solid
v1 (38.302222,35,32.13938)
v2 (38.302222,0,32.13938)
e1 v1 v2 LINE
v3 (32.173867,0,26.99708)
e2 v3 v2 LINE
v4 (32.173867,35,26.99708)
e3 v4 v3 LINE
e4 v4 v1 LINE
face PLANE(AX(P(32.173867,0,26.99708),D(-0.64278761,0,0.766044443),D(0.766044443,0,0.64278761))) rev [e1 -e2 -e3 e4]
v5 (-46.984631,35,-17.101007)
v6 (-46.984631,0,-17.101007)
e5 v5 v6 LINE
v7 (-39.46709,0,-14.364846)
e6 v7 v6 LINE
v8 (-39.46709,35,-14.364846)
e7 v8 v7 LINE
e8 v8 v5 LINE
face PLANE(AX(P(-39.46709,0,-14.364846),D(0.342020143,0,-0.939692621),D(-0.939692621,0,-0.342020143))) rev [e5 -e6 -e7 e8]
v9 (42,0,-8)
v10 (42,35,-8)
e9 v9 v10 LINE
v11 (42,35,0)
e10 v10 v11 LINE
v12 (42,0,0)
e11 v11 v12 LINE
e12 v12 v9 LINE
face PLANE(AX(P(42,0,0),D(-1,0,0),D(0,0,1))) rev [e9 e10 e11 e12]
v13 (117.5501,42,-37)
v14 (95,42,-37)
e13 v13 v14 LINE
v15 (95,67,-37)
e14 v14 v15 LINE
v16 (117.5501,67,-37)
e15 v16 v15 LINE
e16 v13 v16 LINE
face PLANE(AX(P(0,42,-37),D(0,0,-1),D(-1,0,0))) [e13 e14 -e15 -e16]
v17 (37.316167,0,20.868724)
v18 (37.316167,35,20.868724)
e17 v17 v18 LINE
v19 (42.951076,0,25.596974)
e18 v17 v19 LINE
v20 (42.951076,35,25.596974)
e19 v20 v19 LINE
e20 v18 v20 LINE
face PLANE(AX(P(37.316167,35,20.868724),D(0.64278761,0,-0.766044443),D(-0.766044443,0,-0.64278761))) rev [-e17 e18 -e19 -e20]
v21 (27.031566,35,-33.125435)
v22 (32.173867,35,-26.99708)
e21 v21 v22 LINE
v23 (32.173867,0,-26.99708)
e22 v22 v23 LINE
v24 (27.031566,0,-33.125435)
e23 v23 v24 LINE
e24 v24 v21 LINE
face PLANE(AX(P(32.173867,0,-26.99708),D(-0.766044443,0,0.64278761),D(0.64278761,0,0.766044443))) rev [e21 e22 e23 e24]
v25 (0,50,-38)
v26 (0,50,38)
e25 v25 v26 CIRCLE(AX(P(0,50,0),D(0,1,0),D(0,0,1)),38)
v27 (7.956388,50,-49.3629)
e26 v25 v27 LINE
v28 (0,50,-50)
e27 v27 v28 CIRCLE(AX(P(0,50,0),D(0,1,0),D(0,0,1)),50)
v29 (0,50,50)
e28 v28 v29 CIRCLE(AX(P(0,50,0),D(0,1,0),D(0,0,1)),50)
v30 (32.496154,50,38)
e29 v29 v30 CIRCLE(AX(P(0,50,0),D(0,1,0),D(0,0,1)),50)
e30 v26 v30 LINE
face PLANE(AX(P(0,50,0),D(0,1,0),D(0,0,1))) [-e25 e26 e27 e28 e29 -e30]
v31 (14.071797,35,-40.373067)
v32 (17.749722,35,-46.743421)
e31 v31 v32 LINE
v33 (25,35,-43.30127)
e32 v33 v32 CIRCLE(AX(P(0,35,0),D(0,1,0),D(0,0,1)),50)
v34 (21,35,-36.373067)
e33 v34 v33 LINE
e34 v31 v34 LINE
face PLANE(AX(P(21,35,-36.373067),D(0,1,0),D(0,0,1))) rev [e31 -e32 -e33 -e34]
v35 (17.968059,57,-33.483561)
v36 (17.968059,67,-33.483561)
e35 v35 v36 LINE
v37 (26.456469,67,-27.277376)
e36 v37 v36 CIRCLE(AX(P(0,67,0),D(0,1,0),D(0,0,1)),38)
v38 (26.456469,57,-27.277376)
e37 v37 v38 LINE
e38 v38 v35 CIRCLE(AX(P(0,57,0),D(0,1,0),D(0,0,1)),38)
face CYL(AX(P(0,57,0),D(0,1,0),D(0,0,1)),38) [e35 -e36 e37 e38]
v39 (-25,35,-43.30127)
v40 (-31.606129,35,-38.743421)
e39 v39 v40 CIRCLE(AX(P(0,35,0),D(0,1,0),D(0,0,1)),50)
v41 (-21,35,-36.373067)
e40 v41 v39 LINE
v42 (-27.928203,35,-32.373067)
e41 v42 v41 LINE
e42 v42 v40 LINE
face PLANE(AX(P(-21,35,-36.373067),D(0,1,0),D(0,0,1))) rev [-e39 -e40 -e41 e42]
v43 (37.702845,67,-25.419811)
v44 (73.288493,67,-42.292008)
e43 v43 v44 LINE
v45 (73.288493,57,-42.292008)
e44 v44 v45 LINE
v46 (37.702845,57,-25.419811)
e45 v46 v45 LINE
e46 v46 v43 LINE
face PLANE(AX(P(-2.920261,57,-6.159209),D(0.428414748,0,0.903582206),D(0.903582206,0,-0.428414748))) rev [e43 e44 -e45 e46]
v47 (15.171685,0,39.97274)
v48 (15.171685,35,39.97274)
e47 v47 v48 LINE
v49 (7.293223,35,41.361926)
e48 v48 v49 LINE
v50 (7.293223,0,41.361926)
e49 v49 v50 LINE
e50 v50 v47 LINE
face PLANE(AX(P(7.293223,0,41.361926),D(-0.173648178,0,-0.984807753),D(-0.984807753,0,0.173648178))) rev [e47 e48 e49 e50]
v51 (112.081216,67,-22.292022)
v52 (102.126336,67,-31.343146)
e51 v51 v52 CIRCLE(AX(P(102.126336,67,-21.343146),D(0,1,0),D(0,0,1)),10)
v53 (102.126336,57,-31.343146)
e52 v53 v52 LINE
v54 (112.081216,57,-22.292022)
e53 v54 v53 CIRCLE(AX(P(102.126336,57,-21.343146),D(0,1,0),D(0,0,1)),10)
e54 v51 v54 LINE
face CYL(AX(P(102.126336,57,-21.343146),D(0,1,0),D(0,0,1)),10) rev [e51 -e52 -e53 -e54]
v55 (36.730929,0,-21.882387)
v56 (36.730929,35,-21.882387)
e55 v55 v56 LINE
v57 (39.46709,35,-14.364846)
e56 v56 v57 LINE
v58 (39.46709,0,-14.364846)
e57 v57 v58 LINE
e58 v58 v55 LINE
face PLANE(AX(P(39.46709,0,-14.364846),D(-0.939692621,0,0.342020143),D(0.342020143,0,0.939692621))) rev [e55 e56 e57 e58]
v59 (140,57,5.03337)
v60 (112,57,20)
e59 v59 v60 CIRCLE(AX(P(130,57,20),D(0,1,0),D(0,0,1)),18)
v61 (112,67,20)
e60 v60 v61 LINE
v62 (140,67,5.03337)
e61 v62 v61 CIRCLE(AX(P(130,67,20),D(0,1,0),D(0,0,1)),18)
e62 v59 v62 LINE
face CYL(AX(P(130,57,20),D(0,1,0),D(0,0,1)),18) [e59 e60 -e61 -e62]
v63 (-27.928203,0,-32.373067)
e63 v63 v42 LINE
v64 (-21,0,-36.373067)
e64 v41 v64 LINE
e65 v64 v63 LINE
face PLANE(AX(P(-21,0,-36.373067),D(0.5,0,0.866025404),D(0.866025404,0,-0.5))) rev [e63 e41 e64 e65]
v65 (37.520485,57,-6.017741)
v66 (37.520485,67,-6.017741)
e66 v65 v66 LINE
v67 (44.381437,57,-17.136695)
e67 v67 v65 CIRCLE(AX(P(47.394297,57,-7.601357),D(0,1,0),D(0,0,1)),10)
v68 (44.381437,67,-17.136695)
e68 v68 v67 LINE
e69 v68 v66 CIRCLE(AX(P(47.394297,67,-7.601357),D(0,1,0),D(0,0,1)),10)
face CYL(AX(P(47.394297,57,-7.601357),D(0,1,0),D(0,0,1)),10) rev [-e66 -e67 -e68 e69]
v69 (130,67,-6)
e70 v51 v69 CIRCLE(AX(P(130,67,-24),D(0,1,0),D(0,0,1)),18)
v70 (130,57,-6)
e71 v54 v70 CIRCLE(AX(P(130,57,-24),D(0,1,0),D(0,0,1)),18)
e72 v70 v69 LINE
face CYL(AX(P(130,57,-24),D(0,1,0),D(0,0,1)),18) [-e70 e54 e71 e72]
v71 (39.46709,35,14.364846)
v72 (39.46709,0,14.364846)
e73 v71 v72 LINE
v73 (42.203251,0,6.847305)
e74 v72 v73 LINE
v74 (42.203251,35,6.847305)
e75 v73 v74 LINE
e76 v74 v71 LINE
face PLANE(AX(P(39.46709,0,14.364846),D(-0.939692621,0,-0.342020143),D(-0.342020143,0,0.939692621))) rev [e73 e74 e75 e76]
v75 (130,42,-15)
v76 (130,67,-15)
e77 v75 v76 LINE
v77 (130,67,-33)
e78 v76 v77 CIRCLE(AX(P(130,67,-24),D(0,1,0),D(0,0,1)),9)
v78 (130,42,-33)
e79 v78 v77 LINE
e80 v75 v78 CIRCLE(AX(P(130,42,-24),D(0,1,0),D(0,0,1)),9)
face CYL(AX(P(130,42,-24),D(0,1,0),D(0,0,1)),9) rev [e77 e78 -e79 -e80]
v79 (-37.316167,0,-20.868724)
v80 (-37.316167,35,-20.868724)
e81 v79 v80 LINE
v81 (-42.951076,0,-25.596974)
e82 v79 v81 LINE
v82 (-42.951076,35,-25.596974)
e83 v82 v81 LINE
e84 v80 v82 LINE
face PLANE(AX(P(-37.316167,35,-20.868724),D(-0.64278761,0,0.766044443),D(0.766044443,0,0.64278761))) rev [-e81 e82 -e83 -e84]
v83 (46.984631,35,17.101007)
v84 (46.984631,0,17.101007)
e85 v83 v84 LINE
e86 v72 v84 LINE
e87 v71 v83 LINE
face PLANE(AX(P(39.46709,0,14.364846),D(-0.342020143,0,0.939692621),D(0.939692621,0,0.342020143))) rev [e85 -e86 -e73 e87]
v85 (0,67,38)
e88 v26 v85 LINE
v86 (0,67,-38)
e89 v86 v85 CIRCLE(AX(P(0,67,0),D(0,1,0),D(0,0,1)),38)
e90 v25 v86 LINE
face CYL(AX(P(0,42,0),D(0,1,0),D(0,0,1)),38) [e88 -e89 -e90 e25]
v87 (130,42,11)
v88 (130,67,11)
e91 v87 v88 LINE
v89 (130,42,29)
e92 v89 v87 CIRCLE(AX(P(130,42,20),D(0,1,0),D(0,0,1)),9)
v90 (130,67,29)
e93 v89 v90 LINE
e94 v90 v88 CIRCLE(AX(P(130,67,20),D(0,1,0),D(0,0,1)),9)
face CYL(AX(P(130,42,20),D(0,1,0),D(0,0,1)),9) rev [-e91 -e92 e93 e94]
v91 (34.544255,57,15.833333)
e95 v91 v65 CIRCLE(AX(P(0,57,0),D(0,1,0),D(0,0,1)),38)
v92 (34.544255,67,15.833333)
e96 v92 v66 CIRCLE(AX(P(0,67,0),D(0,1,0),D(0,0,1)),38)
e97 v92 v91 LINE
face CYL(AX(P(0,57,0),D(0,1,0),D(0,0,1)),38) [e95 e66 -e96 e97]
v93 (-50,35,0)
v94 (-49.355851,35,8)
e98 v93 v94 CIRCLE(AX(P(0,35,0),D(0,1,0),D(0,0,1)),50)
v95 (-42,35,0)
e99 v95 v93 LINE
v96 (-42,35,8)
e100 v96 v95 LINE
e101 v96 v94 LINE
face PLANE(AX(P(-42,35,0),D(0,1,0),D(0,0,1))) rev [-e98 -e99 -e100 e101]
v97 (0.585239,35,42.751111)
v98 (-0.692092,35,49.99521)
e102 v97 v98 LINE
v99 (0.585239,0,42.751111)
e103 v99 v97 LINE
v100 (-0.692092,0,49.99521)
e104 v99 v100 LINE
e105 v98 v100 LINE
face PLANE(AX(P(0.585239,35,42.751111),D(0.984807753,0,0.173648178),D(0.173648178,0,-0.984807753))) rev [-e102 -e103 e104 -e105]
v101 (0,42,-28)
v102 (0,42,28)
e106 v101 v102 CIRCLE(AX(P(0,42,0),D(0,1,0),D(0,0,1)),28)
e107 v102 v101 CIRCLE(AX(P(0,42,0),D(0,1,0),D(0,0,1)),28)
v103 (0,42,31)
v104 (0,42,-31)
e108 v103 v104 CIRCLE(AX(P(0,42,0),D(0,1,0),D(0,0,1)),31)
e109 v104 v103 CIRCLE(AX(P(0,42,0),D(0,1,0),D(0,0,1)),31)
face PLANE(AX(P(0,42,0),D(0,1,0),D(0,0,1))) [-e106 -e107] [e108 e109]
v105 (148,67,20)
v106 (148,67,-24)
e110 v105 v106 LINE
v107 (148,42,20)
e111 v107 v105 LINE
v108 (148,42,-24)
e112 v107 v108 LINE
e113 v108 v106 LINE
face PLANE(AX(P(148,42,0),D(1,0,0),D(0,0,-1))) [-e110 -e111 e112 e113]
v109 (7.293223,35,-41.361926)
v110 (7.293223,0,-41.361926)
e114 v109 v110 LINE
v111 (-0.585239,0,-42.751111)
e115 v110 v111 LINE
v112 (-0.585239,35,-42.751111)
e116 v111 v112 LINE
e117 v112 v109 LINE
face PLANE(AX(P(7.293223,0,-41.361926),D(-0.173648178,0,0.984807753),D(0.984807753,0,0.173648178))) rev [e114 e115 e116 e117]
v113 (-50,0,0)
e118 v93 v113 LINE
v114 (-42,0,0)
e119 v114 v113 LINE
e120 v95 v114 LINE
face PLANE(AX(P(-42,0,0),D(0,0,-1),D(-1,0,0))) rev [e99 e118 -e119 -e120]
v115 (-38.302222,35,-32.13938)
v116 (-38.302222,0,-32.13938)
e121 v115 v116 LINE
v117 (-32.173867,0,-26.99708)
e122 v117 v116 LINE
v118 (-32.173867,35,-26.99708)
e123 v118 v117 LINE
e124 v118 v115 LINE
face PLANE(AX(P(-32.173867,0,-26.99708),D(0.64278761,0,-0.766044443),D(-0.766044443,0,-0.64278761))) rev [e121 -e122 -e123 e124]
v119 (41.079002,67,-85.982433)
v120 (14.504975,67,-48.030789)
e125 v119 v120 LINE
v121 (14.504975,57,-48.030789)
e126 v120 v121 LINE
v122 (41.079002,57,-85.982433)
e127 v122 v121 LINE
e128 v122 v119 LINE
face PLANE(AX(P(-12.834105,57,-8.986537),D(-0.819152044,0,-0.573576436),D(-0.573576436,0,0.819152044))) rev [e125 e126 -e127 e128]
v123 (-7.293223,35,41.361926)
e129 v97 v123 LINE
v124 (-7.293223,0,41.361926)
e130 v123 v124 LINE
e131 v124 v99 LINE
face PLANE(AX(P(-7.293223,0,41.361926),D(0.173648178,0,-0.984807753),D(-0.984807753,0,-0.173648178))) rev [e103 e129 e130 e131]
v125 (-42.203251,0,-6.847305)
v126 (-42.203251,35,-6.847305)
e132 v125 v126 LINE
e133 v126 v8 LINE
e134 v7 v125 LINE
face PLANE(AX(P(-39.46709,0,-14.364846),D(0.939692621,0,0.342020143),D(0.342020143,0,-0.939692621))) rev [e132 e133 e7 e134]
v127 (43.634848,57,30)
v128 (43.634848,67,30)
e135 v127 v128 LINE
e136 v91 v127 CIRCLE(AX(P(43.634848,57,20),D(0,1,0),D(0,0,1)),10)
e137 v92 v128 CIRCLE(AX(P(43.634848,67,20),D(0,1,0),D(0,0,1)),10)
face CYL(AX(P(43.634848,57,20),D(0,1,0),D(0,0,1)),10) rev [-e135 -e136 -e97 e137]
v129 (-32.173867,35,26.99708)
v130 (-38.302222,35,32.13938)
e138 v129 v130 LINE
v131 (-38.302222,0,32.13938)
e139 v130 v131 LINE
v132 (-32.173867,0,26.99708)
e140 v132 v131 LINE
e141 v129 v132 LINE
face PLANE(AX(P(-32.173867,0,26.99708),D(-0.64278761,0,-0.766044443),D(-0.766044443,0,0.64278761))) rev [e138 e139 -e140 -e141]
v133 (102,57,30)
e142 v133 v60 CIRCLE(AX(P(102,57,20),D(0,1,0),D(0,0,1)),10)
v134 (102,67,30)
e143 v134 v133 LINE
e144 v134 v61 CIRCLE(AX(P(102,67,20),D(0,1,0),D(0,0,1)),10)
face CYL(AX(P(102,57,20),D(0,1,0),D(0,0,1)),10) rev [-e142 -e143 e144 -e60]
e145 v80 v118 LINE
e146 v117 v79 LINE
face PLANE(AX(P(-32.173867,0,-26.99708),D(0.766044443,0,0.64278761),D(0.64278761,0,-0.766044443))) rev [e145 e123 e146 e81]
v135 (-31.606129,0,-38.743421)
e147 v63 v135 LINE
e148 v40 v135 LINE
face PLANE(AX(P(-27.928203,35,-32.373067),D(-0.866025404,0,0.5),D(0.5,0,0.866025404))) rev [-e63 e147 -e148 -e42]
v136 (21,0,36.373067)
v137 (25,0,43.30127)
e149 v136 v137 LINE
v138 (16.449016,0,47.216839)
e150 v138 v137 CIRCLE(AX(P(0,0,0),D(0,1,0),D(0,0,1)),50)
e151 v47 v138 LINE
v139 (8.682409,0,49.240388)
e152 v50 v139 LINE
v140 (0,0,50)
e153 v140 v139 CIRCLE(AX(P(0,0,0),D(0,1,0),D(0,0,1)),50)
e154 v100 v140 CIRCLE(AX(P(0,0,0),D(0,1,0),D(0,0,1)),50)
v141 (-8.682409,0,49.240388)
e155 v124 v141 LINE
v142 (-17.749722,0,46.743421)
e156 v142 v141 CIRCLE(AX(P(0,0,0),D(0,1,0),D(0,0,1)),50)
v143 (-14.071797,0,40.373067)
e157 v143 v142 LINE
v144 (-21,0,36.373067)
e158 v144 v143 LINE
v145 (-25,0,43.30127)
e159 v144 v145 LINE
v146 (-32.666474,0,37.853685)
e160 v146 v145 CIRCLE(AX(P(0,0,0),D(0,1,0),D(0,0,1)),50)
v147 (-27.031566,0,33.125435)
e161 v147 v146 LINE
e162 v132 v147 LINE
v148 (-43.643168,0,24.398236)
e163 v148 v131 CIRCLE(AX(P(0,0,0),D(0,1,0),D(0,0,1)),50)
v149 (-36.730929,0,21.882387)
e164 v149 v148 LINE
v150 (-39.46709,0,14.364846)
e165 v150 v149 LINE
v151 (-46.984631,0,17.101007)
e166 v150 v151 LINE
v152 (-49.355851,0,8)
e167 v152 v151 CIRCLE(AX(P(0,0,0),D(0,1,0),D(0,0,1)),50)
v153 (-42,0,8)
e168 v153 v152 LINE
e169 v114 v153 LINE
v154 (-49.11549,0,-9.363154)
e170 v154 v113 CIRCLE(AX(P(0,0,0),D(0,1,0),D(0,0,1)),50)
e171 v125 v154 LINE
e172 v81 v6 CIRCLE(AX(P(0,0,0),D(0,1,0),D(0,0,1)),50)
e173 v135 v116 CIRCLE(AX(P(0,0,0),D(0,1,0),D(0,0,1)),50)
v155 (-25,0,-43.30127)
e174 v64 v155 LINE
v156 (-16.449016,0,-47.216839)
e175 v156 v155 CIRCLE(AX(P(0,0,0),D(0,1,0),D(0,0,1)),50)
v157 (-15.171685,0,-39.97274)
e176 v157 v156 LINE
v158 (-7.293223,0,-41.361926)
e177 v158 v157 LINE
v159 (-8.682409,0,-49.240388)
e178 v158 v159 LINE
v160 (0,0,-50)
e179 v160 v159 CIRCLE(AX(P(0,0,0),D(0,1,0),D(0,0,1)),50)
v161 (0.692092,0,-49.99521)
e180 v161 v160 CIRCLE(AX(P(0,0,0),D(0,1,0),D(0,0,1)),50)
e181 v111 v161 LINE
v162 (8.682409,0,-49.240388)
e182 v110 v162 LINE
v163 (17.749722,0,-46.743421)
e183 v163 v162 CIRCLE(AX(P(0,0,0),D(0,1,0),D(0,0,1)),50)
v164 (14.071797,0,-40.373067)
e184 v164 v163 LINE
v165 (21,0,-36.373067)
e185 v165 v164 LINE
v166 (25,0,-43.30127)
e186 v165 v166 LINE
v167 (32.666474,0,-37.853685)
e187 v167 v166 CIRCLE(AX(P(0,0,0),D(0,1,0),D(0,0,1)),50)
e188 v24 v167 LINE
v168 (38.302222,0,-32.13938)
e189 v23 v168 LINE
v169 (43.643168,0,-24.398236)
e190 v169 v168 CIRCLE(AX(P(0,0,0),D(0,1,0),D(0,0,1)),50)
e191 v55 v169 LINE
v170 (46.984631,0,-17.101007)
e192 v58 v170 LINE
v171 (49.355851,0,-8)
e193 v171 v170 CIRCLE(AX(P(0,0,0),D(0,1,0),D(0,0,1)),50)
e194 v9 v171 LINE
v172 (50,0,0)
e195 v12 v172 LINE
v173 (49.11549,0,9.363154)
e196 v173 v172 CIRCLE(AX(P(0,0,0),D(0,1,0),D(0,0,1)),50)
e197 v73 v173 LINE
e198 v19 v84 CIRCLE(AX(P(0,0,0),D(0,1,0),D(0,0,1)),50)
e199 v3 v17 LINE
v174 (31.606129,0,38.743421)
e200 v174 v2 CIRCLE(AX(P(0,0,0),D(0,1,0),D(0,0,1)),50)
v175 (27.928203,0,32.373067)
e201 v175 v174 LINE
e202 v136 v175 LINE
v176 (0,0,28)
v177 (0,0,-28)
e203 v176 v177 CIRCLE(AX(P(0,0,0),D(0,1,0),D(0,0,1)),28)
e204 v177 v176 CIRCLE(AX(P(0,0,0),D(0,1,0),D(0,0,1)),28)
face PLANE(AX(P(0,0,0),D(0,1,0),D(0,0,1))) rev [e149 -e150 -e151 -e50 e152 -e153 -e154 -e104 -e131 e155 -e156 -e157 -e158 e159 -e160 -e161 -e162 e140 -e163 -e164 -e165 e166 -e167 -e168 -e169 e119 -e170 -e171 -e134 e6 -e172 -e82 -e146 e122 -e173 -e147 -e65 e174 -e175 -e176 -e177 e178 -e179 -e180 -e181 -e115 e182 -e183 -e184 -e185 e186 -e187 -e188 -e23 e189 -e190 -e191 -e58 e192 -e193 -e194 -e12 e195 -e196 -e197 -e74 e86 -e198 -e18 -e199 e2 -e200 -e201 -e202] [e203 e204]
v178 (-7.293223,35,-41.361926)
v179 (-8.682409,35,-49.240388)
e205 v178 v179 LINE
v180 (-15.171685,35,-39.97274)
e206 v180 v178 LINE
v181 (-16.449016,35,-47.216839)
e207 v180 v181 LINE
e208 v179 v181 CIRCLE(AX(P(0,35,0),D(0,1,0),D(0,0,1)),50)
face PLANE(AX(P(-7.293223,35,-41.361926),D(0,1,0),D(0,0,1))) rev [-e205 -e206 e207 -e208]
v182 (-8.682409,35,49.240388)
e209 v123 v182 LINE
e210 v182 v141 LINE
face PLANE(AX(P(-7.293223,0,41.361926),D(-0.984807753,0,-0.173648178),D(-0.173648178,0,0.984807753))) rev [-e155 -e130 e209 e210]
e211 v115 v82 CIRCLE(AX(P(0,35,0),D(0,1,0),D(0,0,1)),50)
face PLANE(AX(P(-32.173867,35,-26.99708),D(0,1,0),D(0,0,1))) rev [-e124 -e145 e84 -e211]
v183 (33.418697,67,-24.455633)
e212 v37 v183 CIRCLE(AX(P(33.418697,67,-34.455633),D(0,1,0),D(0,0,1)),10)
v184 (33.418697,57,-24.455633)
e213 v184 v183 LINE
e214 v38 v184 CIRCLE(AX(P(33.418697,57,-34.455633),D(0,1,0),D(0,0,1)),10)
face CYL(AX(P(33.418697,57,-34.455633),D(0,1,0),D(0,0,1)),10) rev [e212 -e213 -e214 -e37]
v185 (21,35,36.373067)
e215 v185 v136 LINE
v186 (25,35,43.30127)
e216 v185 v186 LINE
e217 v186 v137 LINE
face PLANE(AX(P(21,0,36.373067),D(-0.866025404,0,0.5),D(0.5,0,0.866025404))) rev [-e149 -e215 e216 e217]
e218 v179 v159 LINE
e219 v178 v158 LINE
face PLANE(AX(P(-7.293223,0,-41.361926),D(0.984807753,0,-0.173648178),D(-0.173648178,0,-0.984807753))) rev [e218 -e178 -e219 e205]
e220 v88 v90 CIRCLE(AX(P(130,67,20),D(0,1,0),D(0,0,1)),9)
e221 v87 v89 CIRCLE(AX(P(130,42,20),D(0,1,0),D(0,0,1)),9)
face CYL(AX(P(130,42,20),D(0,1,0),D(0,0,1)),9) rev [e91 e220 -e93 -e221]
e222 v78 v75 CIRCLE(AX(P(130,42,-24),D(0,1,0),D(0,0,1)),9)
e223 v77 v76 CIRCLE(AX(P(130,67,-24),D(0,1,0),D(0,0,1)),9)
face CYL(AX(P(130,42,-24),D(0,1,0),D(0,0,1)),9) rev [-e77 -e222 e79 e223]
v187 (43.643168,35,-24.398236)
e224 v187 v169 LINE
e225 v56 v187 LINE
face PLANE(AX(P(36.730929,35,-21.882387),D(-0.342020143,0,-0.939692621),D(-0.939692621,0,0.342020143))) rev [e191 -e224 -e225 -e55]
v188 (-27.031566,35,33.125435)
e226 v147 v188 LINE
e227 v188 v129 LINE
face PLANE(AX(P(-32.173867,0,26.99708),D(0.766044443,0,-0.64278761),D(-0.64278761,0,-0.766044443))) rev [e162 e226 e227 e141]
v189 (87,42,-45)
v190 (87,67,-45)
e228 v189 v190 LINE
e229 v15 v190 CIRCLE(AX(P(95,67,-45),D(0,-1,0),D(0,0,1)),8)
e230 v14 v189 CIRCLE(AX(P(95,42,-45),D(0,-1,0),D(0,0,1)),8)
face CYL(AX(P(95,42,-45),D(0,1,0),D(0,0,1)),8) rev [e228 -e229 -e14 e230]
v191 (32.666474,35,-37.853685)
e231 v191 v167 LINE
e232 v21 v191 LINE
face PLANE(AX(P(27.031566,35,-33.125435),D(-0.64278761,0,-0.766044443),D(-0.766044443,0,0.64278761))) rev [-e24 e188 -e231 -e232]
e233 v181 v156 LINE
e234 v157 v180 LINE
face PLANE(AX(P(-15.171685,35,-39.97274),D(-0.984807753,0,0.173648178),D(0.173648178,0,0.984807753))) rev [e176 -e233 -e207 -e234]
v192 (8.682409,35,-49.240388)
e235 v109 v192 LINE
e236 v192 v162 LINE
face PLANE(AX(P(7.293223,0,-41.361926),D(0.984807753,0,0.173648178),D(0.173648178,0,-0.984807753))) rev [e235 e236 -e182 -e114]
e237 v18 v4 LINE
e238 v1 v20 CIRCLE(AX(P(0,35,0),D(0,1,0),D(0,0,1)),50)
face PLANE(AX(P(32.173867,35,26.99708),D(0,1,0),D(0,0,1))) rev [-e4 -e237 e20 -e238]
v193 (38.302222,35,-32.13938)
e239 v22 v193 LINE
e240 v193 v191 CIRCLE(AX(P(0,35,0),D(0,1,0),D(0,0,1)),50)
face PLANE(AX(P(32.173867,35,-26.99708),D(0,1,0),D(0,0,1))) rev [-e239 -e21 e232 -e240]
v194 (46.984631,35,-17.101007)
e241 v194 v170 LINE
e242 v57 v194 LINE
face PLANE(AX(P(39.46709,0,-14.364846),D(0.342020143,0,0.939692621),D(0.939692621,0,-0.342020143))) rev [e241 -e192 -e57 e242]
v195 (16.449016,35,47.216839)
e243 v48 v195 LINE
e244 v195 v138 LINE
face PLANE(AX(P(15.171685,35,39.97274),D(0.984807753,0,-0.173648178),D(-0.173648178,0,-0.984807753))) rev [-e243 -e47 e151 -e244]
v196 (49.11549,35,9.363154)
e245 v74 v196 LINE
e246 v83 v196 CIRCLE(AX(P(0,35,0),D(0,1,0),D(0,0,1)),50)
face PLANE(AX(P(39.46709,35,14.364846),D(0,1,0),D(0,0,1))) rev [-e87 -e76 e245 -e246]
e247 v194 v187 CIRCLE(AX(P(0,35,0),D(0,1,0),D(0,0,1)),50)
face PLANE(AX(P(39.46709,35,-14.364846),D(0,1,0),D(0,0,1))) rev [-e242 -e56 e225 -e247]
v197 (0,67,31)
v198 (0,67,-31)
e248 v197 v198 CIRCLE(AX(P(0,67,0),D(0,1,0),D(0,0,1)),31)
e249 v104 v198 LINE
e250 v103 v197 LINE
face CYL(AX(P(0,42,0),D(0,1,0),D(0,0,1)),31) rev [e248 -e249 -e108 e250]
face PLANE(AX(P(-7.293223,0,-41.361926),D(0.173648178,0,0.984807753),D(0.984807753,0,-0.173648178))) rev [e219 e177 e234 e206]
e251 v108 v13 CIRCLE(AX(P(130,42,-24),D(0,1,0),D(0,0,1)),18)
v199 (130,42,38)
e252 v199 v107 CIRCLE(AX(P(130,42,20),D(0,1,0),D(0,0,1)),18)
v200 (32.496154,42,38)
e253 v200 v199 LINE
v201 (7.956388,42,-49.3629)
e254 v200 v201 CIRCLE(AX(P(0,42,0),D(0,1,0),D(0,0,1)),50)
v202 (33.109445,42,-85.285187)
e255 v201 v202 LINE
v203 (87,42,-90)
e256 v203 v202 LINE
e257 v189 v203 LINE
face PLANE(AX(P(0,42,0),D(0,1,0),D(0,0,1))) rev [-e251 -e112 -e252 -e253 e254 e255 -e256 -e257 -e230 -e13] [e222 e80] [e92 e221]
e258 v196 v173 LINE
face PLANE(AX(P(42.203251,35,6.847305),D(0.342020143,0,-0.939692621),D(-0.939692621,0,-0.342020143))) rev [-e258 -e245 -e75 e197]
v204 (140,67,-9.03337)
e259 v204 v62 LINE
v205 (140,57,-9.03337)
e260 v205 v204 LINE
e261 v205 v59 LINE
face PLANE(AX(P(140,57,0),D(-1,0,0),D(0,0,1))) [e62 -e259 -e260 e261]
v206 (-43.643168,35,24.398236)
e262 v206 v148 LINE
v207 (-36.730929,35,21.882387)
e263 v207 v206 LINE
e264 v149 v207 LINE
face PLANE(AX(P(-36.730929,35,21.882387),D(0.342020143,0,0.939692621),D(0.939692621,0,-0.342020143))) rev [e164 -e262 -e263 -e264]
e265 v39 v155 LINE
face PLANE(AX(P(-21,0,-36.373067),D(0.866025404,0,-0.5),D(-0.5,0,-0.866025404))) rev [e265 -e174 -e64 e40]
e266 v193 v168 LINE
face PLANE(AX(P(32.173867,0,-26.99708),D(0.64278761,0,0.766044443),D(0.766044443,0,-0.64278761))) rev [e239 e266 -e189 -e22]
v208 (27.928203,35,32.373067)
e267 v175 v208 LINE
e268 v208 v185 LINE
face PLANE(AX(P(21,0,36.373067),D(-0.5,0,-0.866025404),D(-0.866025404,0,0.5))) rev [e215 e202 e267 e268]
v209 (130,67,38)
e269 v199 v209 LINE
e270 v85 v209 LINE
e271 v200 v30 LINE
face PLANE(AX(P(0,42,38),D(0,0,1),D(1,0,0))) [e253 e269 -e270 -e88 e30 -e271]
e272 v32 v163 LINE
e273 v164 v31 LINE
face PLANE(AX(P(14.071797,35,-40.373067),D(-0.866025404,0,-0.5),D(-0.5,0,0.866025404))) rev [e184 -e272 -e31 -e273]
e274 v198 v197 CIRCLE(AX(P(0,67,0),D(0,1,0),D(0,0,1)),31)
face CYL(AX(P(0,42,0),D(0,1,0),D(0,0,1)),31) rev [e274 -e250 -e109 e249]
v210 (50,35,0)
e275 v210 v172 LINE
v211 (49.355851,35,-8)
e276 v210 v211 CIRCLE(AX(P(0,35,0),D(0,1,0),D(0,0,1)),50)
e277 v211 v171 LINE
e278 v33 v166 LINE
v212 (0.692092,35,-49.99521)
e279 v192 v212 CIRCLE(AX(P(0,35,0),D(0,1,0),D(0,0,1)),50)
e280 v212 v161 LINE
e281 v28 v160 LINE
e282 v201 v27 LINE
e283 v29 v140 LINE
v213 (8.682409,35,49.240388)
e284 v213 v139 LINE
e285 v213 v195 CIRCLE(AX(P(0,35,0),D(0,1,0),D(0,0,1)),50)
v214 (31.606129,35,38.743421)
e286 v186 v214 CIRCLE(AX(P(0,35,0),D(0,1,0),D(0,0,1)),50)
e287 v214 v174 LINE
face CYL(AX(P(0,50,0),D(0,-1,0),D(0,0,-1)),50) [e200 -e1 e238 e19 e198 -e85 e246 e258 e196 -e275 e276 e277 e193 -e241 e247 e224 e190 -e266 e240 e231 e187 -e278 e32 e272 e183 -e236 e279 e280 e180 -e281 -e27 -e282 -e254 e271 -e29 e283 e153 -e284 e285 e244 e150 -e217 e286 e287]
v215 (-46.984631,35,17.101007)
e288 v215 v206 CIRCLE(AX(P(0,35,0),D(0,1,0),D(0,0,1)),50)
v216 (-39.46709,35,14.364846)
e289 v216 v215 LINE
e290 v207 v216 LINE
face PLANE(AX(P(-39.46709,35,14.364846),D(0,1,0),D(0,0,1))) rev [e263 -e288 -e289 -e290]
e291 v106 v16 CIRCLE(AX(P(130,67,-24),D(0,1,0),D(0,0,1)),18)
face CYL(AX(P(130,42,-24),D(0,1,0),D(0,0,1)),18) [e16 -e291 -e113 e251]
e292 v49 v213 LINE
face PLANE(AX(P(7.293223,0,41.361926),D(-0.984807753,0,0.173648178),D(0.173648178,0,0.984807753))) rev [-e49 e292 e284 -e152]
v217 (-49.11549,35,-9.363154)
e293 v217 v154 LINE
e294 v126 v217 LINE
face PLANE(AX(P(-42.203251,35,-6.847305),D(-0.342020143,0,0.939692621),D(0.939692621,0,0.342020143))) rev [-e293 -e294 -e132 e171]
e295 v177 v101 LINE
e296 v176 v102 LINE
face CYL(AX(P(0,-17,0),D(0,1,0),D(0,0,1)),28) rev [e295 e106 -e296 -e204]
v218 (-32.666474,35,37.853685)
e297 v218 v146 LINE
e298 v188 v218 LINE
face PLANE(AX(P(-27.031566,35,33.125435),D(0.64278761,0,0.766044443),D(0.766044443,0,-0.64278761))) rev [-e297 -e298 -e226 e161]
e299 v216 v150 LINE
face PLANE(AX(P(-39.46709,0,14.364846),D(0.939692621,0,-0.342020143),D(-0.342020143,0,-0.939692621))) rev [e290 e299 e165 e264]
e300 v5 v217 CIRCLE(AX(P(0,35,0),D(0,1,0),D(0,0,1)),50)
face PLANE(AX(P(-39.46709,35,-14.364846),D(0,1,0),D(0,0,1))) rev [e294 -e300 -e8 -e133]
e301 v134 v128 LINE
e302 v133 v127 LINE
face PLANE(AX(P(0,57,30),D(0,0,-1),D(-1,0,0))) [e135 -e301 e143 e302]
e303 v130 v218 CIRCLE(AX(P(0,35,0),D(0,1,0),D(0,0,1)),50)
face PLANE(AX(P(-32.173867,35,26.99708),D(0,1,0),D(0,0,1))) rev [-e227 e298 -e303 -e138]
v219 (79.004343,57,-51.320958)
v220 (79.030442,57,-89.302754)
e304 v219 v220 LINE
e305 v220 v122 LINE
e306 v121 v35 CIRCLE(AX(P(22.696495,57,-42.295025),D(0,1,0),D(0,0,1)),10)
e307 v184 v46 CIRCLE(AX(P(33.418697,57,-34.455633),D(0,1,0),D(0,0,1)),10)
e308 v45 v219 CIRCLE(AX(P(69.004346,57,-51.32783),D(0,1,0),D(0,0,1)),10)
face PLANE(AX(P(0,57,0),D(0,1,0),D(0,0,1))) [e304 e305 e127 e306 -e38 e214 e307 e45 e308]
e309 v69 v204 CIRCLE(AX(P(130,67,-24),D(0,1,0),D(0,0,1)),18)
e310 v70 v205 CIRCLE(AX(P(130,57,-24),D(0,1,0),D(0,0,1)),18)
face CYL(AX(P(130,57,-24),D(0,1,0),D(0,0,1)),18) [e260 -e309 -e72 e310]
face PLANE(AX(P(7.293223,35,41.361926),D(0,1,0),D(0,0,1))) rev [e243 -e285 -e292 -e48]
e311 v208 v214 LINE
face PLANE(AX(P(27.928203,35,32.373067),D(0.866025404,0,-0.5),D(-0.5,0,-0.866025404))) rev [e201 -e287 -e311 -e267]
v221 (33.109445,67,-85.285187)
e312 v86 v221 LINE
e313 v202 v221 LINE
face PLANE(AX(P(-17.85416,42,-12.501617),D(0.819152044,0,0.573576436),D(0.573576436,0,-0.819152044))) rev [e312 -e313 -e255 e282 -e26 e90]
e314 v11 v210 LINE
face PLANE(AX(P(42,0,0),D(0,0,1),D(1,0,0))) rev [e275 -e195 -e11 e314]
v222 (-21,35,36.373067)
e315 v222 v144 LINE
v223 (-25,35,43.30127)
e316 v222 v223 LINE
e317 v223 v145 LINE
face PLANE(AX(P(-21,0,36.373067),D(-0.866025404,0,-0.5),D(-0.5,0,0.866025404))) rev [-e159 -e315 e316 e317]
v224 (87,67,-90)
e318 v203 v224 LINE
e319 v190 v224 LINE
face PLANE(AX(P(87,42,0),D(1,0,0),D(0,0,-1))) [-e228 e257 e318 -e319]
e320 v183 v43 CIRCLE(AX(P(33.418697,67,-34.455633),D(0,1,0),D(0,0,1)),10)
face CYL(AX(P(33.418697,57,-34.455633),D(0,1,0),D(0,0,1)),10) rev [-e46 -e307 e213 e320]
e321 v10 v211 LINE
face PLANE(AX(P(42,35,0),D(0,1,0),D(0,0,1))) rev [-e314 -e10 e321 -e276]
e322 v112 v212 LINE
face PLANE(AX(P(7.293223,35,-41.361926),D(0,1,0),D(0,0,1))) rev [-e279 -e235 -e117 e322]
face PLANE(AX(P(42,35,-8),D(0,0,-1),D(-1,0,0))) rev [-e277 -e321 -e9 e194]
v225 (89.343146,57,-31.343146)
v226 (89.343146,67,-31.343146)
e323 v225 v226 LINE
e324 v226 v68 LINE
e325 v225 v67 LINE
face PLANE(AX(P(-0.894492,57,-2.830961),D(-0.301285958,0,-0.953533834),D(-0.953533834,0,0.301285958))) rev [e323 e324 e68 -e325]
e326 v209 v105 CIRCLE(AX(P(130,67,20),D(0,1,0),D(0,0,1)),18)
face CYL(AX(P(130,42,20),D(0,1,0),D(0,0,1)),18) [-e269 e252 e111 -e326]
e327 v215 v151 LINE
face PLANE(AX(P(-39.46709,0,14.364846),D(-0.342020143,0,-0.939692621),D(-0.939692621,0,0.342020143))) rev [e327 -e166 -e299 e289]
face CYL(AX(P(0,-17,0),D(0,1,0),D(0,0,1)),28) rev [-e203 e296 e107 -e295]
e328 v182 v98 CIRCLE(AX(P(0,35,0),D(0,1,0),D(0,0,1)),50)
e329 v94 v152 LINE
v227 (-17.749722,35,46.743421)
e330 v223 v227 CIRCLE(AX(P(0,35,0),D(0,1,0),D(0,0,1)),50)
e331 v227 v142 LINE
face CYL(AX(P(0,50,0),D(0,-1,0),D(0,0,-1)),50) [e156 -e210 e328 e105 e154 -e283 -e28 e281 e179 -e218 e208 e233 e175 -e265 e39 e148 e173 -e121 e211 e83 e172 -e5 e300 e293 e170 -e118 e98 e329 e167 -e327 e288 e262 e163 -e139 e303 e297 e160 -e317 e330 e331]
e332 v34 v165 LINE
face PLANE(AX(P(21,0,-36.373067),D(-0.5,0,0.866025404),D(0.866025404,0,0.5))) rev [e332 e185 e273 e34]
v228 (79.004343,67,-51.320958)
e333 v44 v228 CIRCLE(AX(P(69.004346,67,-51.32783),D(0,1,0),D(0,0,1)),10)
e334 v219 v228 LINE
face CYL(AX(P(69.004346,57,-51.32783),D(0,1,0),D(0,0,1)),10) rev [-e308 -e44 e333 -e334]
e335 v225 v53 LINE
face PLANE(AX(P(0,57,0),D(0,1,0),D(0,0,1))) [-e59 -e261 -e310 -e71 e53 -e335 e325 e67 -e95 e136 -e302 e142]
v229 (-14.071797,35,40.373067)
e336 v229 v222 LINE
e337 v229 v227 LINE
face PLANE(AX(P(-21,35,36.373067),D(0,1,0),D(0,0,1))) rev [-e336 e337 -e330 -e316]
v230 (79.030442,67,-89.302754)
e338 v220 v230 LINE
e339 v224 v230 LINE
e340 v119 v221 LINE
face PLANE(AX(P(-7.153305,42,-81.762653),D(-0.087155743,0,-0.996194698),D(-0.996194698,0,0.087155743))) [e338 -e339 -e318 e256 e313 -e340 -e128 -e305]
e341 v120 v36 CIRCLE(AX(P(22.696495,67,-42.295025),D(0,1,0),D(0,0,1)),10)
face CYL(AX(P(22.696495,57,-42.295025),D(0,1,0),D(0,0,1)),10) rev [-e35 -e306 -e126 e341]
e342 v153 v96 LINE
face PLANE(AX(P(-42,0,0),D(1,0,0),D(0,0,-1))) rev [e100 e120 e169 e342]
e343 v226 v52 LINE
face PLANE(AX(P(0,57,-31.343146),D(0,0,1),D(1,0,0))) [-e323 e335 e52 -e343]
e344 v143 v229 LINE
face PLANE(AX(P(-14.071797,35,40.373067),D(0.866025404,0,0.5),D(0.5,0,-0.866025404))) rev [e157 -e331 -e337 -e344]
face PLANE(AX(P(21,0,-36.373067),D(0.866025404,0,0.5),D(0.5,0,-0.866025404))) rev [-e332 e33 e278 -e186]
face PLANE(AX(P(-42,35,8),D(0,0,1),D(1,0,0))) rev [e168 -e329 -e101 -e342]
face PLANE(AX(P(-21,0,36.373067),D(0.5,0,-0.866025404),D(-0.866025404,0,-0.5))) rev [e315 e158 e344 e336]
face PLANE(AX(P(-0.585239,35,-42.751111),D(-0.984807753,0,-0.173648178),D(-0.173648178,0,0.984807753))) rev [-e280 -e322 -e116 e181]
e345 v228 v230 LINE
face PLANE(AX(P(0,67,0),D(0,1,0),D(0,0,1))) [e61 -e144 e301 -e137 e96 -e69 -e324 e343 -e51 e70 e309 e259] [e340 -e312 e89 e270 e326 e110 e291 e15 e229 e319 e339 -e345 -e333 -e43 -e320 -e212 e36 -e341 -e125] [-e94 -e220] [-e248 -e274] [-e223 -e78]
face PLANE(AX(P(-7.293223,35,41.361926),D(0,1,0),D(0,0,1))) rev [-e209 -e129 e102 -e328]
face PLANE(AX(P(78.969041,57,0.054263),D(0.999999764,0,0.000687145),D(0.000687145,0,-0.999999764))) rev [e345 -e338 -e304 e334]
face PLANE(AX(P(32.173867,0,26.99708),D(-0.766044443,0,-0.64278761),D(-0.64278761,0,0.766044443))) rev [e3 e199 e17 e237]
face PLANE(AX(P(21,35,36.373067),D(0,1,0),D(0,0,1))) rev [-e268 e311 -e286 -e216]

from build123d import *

# Parameters (mm, degrees)
HUB_PROFILE_SKETCH_R            = 50
HUB_CYLINDER_DEPTH              = 50
GROOVE_PROFILE_SKETCH_W         = 8
GROOVE_PROFILE_SKETCH_H         = 35
RADIAL_GROOVE_DEPTH             = 8
RADIAL_GROOVE_PATTERN_18X_COUNT = 18
BRACKET_ARM_DEPTH               = 17
BRACKET_ARM_DEPTH_BACK          = 8
BRACKET_ARM_SKETCH_R            = 9
ARM_START                       = -10
ARM_POCKETS_DEPTH               = 10
HUB_COUNTERBORE_SKETCH_R        = 31
HUB_COUNTERBORE_DEPTH           = 25
HUB_THROUGH_BORE_SKETCH_R       = 28
HUB_THROUGH_BORE_DEPTH          = 59
POCKET_FILLET_R10_A_R           = 10
POCKET_FILLET_R10_B_R           = 10
POCKET_FILLET_R10_C_R           = 10
POCKET_FILLET_R10_D_R           = 10
POCKET_FILLET_R10_E_R           = 10
POCKET_FILLET_R10_F_R           = 10
POCKET_FILLET_R10_G_R           = 10


with BuildPart() as part:
    # Hub Profile Sketch → Hub Cylinder (new body)
    with BuildSketch(Plane(origin=(0, 0, 0), x_dir=(1, 0, 0), z_dir=(0, 1, 0))):
        with Locations(Location((0, 0, 0), (0, 0, 270))):
            Circle(HUB_PROFILE_SKETCH_R)
    extrude(amount=HUB_CYLINDER_DEPTH)

    # Groove Profile Sketch → Radial Groove (cut)
    with BuildSketch(Plane(origin=(50, 0, 0), x_dir=(0, 0, -1), z_dir=(1, 0, 0))):
        with Locations((4, 17.5)):
            Rectangle(GROOVE_PROFILE_SKETCH_W, GROOVE_PROFILE_SKETCH_H)
    radial_groove = extrude(amount=-RADIAL_GROOVE_DEPTH, mode=Mode.SUBTRACT)

    # Radial Groove Pattern 18x: Radial Groove ×18 about axis
    radial_groove_pattern_18x_axis = Axis((0, 0, 0), (0, 1, 0))
    for i in range(1, RADIAL_GROOVE_PATTERN_18X_COUNT):
        add(radial_groove.rotate(radial_groove_pattern_18x_axis, i * 360 / RADIAL_GROOVE_PATTERN_18X_COUNT), mode=Mode.SUBTRACT)

    # Bracket Arm Sketch → Bracket Arm (add, two sides: drawn at the far end of the back side and taken through both)
    with BuildSketch(Plane(origin=(0, 50, 0), x_dir=(1, 0, 0), z_dir=(0, 1, 0)).offset(-BRACKET_ARM_DEPTH_BACK)):
        with BuildLine():
            Line((33.109444616, 85.285187333), (0, 38))
            ThreePointArc((0, 38), (-38, 0), (0, -38))
            Line((0, -38), (130, -38))
            ThreePointArc((130, -38), (142.727922061, -32.727922061), (148, -20))
            Line((148, -20), (148, 24))
            ThreePointArc((148, 24), (137.067595321, 40.554428301), (117.550100402, 37))
            Line((117.550100402, 37), (95, 37))
            ThreePointArc((95, 37), (89.343145751, 39.343145751), (87, 45))
            Line((87, 45), (87, 90))
            Line((87, 90), (33.109444616, 85.285187333))
        make_face()
        with Locations(Location((130, -20, 0), (0, 0, 270))):
            Circle(BRACKET_ARM_SKETCH_R, mode=Mode.SUBTRACT)
        with Locations(Location((130, 24, 0), (0, 0, 270))):
            Circle(BRACKET_ARM_SKETCH_R, mode=Mode.SUBTRACT)
    extrude(amount=BRACKET_ARM_DEPTH + BRACKET_ARM_DEPTH_BACK)

    # Arm Pocket Sketch → Arm Pockets (cut)
    with BuildSketch(Plane(origin=(0, 67, 0), x_dir=(1, 0, 0), z_dir=(0, 1, 0)).offset(ARM_START)):
        with BuildLine():
            ThreePointArc((38, 0), (34.134327941, -16.698732167), (23.323807579, -30))
            Line((23.323807579, -30), (65, -30))
            Line((65, -30), (115.033370453, -30))
            ThreePointArc((115.033370453, -30), (117.272077939, -7.272077939), (140, -5.033370453))
            Line((140, -5.033370453), (140, 2))
            Line((140, 2), (140, 9.033370453))
            ThreePointArc((140, 9.033370453), (118.390487135, 10.244302597), (113.565943578, 31.343145751))
            Line((113.565943578, 31.343145751), (89.343145751, 31.343145751))
            Line((89.343145751, 31.343145751), (35.229033551, 14.244830468))
            ThreePointArc((35.229033551, 14.244830468), (37.30082623, 7.255919138), (38, 0))
        make_face()
        with BuildLine():
            Line((79.030442415, 89.302754058), (41.079002201, 85.982433275))
            Line((41.079002201, 85.982433275), (7.022974779, 37.345385595))
            ThreePointArc((7.022974779, 37.345385595), (20.403319818, 32.057831187), (30.858927169, 22.17490956))
            Line((30.858927169, 22.17490956), (79, 45))
            Line((79, 45), (79.030442415, 89.302754058))
        make_face()
    extrude(amount=ARM_POCKETS_DEPTH, mode=Mode.SUBTRACT)

    # Hub Counterbore Sketch → Hub Counterbore (cut)
    with BuildSketch(Plane(origin=(0, 67, 0), x_dir=(1, 0, 0), z_dir=(0, 1, 0))):
        with Locations(Location((0, 0, 0), (0, 0, 270))):
            Circle(HUB_COUNTERBORE_SKETCH_R)
    extrude(amount=-HUB_COUNTERBORE_DEPTH, mode=Mode.SUBTRACT)

    # Hub Through Bore Sketch → Hub Through Bore (cut)
    with BuildSketch(Plane(origin=(0, 42, 0), x_dir=(1, 0, 0), z_dir=(0, 1, 0))):
        with Locations(Location((0, 0, 0), (0, 0, 270))):
            Circle(HUB_THROUGH_BORE_SKETCH_R)
    extrude(amount=-HUB_THROUGH_BORE_DEPTH, mode=Mode.SUBTRACT)

    # Pocket Fillet R10 A
    pocket_fillet_r10_a_edges = [part.edges().sort_by_distance(p)[0] for p in [
        (23.323807579, 62, 30),
    ]]
    fillet(pocket_fillet_r10_a_edges, radius=POCKET_FILLET_R10_A_R)

    # Pocket Fillet R10 B
    pocket_fillet_r10_b_edges = [part.edges().sort_by_distance(p)[0] for p in [
        (115.033370453, 62, 30),
    ]]
    fillet(pocket_fillet_r10_b_edges, radius=POCKET_FILLET_R10_B_R)

    # Pocket Fillet R10 C
    pocket_fillet_r10_c_edges = [part.edges().sort_by_distance(p)[0] for p in [
        (113.565943578, 62, -31.343145751),
    ]]
    fillet(pocket_fillet_r10_c_edges, radius=POCKET_FILLET_R10_C_R)

    # Pocket Fillet R10 D
    pocket_fillet_r10_d_edges = [part.edges().sort_by_distance(p)[0] for p in [
        (35.229033551, 62, -14.244830468),
    ]]
    fillet(pocket_fillet_r10_d_edges, radius=POCKET_FILLET_R10_D_R)

    # Pocket Fillet R10 E
    pocket_fillet_r10_e_edges = [part.edges().sort_by_distance(p)[0] for p in [
        (30.858927169, 62, -22.17490956),
    ]]
    fillet(pocket_fillet_r10_e_edges, radius=POCKET_FILLET_R10_E_R)

    # Pocket Fillet R10 F
    pocket_fillet_r10_f_edges = [part.edges().sort_by_distance(p)[0] for p in [
        (79, 62, -45),
    ]]
    fillet(pocket_fillet_r10_f_edges, radius=POCKET_FILLET_R10_F_R)

    # Pocket Fillet R10 G
    pocket_fillet_r10_g_edges = [part.edges().sort_by_distance(p)[0] for p in [
        (7.022974779, 62, -37.345385595),
    ]]
    fillet(pocket_fillet_r10_g_edges, radius=POCKET_FILLET_R10_G_R)


solid = part.part
